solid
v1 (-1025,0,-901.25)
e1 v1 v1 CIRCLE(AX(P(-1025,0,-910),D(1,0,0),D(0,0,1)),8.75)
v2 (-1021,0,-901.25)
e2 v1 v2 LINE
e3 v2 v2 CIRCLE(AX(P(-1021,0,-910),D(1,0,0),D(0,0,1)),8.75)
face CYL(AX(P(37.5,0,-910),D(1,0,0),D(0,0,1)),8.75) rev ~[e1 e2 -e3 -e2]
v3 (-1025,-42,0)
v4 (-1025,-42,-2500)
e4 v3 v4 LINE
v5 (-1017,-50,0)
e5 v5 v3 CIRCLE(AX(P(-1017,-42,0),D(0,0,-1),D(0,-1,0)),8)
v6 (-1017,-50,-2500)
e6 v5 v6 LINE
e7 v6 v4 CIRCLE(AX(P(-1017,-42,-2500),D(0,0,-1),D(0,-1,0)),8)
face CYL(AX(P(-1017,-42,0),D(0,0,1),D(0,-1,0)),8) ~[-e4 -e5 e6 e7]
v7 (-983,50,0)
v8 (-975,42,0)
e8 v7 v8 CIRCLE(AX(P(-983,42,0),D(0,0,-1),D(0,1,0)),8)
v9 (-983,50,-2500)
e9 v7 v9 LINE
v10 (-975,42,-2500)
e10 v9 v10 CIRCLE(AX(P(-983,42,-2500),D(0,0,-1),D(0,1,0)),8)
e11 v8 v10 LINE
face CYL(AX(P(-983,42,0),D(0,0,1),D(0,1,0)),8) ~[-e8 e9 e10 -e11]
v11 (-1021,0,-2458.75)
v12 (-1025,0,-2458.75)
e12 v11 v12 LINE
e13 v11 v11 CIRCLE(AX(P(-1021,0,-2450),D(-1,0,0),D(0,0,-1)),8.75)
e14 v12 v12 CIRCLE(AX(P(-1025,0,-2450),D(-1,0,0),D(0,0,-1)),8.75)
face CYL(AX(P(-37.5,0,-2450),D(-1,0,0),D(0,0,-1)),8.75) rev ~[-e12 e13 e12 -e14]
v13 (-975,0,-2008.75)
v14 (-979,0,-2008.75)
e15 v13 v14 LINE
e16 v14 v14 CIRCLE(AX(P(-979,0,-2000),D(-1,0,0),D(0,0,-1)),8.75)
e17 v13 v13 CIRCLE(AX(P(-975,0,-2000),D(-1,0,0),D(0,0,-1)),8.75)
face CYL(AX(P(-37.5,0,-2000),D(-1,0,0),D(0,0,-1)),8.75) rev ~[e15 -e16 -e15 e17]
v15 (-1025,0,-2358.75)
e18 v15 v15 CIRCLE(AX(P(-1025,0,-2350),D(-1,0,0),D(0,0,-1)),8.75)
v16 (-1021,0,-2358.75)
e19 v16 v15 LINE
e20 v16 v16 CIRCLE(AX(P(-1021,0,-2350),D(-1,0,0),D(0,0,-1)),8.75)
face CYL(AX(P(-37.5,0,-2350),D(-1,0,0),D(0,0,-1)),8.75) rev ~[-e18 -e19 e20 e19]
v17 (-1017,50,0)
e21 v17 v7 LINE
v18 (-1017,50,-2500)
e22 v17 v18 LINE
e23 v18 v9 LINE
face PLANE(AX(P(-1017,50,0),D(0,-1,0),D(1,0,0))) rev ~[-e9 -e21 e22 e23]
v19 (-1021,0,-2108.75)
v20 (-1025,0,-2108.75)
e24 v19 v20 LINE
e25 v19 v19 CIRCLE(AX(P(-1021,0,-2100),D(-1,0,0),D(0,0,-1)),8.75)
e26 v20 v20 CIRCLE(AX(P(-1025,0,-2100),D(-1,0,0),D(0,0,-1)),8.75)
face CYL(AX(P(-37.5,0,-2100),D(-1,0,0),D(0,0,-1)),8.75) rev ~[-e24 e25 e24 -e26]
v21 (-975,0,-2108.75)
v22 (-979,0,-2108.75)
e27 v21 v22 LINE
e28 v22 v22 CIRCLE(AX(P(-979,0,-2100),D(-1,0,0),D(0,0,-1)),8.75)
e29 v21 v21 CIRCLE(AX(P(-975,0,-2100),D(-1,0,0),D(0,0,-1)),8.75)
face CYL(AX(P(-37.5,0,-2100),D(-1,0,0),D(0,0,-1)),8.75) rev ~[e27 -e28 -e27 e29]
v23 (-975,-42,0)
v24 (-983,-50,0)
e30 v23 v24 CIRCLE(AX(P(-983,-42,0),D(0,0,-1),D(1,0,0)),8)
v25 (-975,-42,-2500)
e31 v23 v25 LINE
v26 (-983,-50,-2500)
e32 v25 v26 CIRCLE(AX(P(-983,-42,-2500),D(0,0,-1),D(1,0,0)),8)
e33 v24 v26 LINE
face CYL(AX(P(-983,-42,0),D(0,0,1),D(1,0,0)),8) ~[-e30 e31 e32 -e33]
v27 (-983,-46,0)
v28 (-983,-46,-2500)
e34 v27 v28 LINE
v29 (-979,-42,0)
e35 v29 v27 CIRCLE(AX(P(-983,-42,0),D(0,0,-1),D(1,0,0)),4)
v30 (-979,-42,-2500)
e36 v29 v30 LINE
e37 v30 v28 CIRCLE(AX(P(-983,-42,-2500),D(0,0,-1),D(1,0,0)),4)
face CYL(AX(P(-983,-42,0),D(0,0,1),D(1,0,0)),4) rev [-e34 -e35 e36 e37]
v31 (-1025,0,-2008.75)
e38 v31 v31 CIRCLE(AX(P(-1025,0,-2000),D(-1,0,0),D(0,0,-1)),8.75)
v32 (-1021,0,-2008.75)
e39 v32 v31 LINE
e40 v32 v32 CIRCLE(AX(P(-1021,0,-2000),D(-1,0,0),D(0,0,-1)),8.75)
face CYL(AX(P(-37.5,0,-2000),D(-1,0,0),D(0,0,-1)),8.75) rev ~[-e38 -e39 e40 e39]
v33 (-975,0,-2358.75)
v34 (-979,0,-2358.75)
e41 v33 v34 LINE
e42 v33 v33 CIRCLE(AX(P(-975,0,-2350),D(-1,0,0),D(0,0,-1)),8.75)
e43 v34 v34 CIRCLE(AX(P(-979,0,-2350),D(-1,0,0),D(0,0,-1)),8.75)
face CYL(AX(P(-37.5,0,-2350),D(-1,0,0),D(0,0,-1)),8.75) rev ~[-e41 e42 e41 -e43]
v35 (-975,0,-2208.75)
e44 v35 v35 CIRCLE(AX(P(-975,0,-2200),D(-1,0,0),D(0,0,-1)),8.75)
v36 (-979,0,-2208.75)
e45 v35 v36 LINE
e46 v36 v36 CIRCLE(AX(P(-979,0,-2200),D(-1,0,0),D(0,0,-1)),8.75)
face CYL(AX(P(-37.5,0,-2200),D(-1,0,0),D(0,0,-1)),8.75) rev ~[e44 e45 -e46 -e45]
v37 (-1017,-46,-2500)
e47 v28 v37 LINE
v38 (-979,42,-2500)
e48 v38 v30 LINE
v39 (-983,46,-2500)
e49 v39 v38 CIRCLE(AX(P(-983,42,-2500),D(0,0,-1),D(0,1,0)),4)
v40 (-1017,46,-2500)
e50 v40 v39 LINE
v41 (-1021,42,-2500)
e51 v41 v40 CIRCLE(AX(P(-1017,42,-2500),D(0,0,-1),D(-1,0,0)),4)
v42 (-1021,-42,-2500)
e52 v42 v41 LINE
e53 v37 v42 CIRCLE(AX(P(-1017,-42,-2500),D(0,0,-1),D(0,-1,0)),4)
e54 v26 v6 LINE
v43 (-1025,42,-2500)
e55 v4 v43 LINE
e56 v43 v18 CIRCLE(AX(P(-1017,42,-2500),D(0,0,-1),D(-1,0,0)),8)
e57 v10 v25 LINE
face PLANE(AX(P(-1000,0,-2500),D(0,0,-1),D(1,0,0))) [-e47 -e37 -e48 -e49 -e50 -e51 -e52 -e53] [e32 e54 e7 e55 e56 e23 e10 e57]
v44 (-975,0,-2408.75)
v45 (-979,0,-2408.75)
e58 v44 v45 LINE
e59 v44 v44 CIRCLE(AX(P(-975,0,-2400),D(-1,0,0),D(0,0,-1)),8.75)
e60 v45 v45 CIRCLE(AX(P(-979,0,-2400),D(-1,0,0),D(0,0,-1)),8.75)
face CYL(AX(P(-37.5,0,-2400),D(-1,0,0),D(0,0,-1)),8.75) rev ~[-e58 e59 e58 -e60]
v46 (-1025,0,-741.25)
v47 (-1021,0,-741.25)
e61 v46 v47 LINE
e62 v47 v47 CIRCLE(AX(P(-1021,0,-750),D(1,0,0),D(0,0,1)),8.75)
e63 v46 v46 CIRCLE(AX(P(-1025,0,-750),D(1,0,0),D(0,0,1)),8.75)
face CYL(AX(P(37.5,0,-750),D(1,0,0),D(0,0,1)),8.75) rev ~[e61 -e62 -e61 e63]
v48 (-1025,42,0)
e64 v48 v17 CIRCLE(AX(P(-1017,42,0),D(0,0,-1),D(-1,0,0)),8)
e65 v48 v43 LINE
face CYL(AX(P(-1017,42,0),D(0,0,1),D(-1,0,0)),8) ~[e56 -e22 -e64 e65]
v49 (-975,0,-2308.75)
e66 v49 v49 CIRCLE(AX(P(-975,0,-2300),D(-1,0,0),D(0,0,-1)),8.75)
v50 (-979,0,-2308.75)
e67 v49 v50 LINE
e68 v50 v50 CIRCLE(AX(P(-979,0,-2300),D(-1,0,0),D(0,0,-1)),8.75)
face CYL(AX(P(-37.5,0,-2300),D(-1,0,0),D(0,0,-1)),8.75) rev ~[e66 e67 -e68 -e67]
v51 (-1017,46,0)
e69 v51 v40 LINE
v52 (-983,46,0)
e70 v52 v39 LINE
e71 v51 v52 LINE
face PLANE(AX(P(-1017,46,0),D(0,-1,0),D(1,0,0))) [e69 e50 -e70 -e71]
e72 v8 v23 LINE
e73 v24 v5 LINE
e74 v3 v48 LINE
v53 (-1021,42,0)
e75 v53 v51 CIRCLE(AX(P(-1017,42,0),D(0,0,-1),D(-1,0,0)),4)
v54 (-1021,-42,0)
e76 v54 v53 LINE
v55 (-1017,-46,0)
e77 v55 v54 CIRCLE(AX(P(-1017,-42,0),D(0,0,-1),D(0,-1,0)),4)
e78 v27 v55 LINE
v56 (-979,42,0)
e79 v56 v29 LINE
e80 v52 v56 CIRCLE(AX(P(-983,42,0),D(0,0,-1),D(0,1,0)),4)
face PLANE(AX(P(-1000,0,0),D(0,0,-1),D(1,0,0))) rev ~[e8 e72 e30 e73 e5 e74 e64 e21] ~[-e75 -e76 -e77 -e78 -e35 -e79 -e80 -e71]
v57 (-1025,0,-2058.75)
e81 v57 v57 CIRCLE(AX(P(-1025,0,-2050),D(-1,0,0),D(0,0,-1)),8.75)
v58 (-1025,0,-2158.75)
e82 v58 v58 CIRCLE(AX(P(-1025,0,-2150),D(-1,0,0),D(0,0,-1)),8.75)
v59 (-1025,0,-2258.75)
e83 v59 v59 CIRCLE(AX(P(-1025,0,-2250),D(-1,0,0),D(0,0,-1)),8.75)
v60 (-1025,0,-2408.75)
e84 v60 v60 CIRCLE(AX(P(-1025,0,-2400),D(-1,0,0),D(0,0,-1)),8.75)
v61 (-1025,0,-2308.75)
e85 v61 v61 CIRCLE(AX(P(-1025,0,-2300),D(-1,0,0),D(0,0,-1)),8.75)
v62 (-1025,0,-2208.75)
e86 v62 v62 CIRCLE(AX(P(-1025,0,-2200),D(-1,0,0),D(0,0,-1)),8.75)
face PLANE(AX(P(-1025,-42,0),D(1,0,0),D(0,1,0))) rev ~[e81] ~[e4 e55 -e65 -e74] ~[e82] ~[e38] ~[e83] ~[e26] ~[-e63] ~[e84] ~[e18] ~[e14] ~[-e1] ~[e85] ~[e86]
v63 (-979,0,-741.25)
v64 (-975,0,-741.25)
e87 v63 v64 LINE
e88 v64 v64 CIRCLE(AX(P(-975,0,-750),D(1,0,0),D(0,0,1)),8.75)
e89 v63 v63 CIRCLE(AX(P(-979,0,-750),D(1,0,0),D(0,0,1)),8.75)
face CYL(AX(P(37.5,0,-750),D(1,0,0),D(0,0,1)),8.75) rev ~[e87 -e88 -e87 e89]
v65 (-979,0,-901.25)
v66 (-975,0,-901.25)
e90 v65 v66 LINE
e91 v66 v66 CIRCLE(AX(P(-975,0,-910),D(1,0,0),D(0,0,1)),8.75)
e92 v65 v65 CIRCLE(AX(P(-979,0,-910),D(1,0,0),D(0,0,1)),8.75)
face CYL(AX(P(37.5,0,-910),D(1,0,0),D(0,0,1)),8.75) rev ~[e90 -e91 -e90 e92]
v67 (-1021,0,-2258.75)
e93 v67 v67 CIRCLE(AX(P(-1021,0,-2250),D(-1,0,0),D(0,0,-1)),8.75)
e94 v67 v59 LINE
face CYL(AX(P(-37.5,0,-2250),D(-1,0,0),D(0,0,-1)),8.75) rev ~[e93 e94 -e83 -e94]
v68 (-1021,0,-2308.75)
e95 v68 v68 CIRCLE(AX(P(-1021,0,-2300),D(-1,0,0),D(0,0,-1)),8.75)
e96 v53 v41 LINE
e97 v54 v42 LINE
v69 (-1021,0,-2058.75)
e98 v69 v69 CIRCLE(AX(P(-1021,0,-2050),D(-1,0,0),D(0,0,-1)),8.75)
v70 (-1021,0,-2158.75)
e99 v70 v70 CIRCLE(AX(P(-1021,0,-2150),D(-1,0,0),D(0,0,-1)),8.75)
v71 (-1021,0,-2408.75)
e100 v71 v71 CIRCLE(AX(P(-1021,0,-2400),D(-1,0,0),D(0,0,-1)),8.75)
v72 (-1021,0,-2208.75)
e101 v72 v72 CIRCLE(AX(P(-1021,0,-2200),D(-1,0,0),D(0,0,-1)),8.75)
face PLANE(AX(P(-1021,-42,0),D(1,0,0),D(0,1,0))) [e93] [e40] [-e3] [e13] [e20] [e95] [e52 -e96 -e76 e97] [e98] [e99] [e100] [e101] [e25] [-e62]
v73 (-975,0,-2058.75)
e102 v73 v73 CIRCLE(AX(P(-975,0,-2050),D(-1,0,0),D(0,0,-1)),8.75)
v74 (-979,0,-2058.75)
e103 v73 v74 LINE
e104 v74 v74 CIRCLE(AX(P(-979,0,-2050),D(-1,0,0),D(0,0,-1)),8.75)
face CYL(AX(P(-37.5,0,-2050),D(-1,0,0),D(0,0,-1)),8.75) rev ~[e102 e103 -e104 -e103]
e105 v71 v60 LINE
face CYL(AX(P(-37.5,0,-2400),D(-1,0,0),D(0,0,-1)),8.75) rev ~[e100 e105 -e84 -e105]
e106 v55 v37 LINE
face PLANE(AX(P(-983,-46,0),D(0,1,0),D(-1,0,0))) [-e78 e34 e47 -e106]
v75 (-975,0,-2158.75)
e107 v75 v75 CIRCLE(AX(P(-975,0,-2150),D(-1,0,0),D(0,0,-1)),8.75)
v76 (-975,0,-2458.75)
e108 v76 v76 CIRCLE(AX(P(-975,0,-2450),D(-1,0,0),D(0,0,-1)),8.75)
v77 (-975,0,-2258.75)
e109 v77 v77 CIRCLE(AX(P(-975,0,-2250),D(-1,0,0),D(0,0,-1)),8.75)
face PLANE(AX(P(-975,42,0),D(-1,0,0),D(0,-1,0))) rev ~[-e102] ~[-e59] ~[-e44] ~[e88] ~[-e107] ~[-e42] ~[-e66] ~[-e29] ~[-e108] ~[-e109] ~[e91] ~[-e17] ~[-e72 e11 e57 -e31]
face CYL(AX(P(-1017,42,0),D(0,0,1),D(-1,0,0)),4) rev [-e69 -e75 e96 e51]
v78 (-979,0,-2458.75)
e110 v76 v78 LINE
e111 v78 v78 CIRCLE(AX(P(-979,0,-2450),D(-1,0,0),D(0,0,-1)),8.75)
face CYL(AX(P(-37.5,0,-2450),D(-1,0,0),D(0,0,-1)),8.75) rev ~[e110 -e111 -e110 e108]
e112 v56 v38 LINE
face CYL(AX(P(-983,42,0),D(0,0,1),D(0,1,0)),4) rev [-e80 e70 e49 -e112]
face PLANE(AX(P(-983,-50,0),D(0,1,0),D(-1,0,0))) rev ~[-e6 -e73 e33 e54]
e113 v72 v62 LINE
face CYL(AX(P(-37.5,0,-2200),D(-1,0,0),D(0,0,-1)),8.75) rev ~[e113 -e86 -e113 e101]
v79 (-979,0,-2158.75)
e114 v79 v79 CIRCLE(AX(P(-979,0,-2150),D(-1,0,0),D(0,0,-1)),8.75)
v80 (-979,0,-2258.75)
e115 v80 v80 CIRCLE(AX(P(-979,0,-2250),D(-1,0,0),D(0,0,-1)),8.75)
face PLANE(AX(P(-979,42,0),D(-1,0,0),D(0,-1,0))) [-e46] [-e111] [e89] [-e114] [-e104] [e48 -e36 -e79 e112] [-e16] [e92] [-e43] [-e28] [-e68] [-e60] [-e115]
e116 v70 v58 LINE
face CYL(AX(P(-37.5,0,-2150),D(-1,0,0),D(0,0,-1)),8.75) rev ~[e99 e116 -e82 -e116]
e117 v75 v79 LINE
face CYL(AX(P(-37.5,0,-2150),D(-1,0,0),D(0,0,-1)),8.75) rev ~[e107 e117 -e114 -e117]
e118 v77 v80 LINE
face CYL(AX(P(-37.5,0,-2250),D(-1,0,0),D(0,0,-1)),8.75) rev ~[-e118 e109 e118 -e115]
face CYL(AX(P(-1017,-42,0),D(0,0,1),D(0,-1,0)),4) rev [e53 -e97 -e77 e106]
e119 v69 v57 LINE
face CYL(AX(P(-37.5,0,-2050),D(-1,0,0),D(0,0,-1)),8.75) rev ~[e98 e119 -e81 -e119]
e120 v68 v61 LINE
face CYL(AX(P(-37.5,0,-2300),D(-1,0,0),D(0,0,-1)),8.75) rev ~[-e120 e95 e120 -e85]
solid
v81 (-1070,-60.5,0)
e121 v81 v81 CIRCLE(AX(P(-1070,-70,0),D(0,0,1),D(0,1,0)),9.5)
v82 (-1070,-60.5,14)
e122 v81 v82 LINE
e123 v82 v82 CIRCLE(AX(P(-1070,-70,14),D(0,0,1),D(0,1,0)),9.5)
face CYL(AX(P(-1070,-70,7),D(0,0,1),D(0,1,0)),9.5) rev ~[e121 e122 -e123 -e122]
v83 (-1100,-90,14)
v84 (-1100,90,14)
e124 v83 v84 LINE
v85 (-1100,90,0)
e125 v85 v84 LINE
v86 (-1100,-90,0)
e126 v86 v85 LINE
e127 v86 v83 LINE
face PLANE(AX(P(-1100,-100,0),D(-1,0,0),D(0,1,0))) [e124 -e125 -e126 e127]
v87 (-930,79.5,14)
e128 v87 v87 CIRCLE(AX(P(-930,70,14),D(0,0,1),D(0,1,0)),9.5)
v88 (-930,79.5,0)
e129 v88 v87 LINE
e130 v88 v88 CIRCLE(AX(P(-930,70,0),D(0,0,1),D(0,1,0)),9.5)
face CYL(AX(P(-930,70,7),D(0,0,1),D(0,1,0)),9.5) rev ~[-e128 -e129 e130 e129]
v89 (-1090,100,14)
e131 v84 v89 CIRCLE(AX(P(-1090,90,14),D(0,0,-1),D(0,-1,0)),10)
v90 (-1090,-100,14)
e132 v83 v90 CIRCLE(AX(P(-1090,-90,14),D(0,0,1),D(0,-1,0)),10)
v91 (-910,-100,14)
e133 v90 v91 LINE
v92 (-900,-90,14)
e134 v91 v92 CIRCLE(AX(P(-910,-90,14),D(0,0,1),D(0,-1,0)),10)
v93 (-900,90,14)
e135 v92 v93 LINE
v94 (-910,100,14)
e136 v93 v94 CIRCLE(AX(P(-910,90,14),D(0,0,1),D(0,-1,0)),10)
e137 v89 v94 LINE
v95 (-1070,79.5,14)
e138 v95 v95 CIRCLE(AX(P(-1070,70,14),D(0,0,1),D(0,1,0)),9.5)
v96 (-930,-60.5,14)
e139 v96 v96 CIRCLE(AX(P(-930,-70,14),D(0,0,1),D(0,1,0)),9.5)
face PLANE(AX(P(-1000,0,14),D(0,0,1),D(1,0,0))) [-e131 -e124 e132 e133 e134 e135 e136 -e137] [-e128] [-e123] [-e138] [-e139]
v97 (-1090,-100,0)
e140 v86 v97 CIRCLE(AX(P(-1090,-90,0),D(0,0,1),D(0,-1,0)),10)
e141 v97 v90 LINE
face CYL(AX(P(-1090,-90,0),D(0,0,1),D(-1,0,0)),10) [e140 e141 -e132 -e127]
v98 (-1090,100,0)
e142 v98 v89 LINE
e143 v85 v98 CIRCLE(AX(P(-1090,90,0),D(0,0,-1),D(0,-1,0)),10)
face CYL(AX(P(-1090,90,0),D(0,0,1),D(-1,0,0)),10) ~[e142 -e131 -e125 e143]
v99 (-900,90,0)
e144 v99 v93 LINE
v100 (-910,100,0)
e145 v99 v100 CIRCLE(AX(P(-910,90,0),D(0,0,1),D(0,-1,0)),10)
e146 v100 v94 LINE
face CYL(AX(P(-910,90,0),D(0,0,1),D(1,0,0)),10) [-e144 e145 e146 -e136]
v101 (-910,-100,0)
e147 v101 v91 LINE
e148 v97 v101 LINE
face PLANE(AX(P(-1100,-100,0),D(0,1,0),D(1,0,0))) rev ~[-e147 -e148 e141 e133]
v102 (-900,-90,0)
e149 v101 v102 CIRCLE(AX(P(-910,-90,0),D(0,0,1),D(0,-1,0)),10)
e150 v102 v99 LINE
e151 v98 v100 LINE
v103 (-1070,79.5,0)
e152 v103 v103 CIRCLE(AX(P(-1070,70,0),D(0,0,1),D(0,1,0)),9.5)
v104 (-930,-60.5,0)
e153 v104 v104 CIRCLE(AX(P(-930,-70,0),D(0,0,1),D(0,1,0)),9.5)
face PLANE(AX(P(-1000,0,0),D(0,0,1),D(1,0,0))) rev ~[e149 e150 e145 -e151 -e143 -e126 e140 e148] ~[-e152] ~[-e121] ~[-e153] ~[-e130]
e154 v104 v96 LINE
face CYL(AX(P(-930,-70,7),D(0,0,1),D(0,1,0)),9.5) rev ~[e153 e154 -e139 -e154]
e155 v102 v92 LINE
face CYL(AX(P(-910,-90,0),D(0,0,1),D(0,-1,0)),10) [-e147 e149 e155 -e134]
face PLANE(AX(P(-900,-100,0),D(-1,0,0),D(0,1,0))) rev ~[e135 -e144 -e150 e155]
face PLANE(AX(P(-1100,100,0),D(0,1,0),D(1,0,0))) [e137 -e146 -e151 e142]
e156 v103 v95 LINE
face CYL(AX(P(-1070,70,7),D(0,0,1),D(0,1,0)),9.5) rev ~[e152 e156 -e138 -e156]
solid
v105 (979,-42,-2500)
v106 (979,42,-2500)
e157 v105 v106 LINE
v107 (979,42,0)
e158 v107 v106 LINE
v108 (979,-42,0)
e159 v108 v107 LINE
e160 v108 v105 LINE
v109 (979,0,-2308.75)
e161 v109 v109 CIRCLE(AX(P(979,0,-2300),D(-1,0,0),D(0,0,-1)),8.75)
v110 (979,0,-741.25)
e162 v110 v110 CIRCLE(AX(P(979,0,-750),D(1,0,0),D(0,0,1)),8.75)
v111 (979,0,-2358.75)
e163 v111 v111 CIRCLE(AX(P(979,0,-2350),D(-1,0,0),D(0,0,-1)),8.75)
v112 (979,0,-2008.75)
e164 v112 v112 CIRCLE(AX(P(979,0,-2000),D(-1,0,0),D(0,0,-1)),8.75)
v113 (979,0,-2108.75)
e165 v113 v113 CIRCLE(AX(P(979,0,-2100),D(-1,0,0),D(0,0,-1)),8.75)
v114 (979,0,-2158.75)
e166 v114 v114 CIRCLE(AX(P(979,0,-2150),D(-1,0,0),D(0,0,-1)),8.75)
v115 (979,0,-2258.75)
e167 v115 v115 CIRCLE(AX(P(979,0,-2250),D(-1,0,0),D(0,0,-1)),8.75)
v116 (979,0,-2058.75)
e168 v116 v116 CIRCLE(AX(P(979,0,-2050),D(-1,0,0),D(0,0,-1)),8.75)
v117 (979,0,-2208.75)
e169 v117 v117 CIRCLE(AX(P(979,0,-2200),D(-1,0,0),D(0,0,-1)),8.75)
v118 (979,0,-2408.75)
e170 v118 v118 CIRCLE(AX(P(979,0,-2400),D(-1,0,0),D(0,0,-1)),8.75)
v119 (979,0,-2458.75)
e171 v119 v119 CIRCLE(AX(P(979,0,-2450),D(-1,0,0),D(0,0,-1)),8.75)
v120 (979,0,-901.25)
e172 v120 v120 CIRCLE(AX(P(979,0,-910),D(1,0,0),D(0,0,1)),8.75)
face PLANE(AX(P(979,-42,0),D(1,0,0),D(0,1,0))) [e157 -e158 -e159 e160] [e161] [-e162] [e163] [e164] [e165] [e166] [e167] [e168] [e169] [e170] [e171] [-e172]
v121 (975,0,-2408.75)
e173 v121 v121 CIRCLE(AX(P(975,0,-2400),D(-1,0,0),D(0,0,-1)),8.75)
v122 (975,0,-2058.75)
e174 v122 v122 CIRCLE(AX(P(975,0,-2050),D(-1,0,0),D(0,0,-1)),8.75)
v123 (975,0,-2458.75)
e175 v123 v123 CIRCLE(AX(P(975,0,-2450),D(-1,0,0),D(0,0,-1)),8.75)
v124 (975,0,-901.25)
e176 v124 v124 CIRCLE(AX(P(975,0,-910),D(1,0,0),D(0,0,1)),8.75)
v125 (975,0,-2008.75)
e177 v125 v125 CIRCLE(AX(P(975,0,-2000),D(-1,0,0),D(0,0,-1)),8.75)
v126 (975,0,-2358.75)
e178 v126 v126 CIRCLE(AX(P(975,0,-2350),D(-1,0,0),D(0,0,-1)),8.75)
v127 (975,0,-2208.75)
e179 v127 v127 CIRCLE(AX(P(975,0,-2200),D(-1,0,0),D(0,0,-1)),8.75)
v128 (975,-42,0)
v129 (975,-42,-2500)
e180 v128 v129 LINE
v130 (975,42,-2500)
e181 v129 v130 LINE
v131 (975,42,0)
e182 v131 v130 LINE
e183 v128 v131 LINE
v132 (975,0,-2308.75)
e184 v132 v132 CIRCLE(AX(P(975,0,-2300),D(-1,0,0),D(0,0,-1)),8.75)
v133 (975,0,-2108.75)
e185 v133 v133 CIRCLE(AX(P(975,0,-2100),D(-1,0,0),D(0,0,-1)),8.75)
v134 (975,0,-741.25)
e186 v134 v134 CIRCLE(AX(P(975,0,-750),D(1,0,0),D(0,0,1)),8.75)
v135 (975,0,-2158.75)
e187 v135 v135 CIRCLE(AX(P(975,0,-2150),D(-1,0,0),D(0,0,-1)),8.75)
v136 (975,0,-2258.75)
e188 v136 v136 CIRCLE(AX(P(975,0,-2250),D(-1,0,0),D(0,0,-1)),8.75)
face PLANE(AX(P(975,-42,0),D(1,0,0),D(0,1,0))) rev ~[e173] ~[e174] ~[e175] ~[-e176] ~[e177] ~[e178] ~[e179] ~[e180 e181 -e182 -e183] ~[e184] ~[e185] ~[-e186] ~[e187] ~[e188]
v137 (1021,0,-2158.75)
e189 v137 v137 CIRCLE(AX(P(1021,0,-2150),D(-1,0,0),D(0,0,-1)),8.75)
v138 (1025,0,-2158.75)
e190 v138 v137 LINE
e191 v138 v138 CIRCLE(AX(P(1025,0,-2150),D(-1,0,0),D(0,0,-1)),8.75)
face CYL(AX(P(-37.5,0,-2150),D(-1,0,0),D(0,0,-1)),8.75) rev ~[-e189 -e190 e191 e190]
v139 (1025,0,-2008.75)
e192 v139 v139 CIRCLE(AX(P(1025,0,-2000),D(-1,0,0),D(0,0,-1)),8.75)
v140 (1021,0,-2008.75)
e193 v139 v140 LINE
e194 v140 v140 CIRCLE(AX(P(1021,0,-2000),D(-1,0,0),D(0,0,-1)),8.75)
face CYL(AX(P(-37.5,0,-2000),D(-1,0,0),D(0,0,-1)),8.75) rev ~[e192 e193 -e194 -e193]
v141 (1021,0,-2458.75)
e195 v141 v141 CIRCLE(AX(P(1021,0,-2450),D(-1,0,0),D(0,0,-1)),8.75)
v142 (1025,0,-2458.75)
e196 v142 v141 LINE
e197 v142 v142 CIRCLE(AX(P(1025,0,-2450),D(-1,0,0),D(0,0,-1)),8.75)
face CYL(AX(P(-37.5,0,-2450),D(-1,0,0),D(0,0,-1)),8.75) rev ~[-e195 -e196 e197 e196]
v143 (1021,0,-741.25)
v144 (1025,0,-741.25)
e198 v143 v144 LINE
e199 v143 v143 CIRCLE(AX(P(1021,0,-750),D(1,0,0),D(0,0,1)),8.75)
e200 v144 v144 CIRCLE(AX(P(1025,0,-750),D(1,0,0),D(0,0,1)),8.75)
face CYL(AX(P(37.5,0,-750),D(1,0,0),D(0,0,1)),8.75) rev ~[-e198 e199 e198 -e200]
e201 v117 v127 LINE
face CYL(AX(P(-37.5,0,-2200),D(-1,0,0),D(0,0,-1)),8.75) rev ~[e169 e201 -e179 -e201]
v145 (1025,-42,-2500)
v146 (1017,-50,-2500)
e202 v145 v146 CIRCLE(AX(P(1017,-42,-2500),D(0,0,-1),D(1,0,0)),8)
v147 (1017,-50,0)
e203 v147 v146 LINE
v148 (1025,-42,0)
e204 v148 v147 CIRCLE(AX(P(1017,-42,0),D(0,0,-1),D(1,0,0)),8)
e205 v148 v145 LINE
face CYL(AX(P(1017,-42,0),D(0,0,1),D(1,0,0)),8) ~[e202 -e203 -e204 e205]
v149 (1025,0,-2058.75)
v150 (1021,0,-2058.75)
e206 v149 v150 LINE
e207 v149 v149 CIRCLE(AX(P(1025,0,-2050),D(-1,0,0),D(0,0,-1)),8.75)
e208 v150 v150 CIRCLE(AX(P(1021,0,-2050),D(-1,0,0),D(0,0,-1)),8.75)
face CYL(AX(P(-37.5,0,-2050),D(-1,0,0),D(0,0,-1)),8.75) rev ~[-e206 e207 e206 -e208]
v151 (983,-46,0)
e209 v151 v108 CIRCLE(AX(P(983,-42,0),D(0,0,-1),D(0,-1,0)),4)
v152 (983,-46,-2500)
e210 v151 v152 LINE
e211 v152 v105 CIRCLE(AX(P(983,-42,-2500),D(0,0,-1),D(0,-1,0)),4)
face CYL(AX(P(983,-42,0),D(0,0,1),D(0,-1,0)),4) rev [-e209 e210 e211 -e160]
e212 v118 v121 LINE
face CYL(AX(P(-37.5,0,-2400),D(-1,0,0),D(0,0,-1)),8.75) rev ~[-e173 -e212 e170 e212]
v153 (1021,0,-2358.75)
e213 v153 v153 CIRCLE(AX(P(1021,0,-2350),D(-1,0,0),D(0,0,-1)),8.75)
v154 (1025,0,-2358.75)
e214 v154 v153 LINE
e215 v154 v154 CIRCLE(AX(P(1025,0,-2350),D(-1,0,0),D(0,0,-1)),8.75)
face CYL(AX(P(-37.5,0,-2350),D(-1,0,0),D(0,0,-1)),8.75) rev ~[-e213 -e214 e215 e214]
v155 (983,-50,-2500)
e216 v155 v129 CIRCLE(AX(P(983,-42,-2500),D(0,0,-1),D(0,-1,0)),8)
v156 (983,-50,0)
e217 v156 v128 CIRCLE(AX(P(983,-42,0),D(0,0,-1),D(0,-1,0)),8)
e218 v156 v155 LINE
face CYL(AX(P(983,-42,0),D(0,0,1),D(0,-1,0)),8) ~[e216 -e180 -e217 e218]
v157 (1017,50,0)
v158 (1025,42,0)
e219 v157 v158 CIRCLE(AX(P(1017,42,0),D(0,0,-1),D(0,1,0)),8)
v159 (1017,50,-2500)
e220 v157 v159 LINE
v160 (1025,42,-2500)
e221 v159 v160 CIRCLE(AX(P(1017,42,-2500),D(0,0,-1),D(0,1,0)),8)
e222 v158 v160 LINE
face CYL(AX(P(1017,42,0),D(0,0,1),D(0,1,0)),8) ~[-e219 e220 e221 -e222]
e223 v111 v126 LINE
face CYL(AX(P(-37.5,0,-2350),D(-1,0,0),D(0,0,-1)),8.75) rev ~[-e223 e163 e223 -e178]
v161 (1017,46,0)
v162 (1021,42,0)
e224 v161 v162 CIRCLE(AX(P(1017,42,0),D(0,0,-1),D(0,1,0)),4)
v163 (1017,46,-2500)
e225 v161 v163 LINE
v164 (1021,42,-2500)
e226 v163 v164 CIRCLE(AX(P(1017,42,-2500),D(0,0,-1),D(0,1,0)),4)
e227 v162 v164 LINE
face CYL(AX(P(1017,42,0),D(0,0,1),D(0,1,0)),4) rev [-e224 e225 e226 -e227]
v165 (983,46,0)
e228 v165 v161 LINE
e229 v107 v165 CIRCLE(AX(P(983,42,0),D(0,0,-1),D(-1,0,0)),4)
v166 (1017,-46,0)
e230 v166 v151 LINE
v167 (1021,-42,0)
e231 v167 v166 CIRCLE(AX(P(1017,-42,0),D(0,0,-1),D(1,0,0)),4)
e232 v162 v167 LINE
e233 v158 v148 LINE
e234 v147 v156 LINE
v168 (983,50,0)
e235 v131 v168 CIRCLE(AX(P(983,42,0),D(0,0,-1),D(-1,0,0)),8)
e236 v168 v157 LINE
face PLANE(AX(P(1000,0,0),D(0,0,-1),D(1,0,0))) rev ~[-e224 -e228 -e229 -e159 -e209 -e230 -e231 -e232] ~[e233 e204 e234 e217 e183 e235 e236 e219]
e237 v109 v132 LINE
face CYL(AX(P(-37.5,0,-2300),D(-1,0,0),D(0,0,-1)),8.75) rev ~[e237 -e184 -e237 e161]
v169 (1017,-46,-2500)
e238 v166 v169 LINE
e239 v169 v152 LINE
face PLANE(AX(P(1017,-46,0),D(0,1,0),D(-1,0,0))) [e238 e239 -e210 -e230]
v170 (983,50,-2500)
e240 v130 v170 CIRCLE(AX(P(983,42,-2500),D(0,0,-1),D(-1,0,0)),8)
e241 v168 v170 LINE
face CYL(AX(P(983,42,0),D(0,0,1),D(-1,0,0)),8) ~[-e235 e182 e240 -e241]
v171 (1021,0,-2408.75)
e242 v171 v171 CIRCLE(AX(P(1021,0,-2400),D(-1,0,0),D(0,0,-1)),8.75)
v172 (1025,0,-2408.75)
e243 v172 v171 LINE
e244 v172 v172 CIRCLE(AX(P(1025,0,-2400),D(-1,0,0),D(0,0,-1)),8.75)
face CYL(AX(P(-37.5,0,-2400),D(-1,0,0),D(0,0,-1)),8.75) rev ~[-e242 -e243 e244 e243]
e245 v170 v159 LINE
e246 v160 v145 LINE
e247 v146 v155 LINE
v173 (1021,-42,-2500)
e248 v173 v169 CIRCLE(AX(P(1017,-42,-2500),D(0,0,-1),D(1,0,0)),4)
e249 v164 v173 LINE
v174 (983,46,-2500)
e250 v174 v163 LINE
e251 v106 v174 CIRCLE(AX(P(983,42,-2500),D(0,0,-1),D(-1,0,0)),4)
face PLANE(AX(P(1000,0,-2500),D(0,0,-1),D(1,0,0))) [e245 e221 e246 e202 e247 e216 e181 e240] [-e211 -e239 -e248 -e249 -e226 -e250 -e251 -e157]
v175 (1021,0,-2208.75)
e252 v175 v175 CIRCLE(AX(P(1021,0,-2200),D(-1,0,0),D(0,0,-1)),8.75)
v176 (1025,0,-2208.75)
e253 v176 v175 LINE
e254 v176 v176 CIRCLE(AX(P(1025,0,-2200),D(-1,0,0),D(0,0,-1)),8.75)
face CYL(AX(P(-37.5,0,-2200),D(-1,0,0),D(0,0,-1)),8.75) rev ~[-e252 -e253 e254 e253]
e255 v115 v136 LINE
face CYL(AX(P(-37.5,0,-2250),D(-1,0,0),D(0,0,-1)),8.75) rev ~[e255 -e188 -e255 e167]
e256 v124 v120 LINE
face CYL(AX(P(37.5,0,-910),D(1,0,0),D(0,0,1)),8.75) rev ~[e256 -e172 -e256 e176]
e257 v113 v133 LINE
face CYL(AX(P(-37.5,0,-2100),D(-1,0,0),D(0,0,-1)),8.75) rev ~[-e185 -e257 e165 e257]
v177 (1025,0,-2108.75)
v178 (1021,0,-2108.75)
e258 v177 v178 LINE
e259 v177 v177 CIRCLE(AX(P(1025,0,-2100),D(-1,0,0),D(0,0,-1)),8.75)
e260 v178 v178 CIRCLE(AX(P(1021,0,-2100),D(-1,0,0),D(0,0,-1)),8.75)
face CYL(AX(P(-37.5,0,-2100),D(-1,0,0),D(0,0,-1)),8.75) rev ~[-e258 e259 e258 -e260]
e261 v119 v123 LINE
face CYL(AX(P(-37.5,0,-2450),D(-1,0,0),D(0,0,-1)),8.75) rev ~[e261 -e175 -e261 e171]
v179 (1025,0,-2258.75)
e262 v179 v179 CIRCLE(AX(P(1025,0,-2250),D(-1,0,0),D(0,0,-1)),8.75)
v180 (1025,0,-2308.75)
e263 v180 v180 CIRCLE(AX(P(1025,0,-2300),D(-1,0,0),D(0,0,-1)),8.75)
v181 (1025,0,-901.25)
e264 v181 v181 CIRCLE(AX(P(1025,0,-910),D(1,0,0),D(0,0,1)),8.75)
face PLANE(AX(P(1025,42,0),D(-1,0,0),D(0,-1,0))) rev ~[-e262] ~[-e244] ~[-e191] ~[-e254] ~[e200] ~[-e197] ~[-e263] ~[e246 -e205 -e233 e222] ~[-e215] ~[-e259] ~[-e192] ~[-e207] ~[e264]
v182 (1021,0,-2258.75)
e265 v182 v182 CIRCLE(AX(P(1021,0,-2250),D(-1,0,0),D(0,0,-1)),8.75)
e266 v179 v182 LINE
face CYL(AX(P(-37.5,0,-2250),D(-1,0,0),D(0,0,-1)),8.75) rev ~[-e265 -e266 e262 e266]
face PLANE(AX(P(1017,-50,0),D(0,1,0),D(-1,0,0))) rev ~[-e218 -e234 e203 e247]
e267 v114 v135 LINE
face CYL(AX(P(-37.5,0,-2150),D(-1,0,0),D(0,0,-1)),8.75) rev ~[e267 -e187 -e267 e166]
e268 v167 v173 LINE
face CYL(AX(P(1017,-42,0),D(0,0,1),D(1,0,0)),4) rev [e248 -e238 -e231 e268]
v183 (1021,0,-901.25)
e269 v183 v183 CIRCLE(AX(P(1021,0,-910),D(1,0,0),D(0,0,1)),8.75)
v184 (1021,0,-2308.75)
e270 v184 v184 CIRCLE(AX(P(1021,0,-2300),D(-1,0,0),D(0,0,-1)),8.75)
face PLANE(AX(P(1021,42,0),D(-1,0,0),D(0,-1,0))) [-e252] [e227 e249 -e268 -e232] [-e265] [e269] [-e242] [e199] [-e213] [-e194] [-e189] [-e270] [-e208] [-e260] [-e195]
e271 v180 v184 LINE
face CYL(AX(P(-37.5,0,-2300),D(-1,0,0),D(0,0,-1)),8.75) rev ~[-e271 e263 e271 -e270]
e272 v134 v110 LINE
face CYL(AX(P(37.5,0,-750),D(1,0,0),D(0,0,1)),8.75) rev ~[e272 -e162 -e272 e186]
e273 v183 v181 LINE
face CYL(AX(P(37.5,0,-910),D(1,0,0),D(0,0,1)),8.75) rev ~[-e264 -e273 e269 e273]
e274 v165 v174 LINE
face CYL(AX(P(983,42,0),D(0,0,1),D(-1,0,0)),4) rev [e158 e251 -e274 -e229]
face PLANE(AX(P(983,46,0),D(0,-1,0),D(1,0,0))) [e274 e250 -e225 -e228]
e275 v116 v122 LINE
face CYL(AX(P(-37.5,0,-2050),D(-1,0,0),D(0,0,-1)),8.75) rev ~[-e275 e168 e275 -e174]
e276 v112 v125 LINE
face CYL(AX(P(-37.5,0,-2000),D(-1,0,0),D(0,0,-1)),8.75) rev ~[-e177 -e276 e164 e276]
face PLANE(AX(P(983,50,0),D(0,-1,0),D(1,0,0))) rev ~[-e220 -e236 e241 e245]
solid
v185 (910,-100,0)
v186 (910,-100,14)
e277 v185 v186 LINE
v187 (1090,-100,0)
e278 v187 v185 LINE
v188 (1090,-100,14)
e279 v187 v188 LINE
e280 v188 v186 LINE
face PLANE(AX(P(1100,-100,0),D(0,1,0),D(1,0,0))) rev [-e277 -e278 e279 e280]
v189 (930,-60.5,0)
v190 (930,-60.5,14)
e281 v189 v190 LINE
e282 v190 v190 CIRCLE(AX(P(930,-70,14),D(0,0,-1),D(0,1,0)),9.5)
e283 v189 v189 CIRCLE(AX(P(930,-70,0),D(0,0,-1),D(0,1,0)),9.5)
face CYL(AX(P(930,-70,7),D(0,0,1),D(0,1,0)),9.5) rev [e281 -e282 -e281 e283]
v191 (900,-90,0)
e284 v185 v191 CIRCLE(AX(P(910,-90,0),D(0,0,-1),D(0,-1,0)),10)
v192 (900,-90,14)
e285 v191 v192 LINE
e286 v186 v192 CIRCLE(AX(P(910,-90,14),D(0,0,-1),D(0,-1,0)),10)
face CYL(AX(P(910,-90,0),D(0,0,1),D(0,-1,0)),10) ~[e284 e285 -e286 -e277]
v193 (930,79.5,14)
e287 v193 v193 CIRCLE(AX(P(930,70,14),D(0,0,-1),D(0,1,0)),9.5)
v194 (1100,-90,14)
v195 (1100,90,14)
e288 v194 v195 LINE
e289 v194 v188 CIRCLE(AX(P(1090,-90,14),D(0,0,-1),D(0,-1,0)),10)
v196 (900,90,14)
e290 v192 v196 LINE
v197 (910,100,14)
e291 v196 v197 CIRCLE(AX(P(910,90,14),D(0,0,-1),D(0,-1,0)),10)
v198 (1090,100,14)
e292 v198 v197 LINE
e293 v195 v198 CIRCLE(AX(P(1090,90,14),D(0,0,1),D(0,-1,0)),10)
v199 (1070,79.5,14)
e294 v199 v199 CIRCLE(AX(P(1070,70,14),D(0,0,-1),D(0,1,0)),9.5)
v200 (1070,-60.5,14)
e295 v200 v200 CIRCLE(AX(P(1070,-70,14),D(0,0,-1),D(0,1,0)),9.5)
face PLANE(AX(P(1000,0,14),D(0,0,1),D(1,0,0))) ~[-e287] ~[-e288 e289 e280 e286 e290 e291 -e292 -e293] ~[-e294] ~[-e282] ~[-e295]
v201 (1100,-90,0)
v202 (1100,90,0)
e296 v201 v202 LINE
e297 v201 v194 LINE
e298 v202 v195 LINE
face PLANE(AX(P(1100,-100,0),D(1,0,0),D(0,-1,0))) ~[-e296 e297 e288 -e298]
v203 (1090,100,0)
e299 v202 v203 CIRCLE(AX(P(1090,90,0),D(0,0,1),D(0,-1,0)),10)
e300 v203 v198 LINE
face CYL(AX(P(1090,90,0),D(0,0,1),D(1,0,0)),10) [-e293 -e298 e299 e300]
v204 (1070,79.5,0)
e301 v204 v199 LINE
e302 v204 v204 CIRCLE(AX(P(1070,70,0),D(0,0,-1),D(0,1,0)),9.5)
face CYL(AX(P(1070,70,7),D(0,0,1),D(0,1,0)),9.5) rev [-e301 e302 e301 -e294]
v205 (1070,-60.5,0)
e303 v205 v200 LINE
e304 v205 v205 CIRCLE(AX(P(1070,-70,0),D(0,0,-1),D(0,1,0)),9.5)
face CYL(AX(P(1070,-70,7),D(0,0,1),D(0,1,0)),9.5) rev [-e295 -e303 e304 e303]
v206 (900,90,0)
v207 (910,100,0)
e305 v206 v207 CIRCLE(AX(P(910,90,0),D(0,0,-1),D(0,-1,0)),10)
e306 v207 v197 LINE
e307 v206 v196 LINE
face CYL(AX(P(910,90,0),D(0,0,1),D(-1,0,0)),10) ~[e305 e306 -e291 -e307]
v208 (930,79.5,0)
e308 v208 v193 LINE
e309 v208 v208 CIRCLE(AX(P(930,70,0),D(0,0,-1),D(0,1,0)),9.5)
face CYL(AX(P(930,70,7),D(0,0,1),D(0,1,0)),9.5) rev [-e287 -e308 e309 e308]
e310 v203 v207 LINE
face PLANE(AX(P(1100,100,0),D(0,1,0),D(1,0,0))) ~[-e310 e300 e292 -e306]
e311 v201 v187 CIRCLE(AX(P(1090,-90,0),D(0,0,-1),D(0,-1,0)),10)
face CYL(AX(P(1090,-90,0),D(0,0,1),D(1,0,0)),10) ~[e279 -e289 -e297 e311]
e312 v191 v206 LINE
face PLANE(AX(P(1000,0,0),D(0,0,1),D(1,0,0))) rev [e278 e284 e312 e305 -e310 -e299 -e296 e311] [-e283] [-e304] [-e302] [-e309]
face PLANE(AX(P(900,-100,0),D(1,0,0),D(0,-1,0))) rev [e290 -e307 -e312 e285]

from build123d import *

# Parameters (mm, degrees)
GB_6728_1986_RECTANGULAR_HOLLOW_SECTION_DEPTH = 2500
GB_6728_1986_RECTANGULAR_HOLLOW_SECT_2_DEPTH  = 2500
SKETCH5_W                                     = 200
SKETCH5_H                                     = 200
BOSS_EXTRUDE1_DEPTH                           = 14
FILLET1_R                                     = 10
SKETCH9_W                                     = 9.5
SKETCH9_H                                     = 14
M16_CLEARANCE_HOLE1_AT_2_COUNT                = 2
M16_CLEARANCE_HOLE1_AT_2_PITCH                = 140
M16_CLEARANCE_HOLE1_AT_3_COUNT                = 2
M16_CLEARANCE_HOLE1_AT_3_PITCH                = 197.989898732
M16_CLEARANCE_HOLE1_AT_4_COUNT                = 2
M16_CLEARANCE_HOLE1_AT_4_PITCH                = 140
SKETCH14_W                                    = 8.75
SKETCH14_H                                    = 2125
LPATTERN1_COUNT                               = 10
LPATTERN1_PITCH                               = 50
SKETCH16_W                                    = 8.75
SKETCH16_H                                    = 2125
M16_CLEARANCE_HOLE4_AT_2_COUNT                = 2
M16_CLEARANCE_HOLE4_AT_2_PITCH                = 160


with BuildPart() as part:
    # Sketch12 → Gb／6728-1986 rectangular hollow section 100 X 50 X 4 (1) (new body)
    with BuildSketch(Plane(origin=(-1000, 0, 0), x_dir=(1, 0, 0), z_dir=(0, 0, -1))):
        with BuildLine():
            Line((-17, -50), (17, -50))
            ThreePointArc((17, -50), (22.656854249, -47.656854249), (25, -42))
            Line((25, -42), (25, 42))
            ThreePointArc((25, 42), (22.656854249, 47.656854249), (17, 50))
            Line((17, 50), (-17, 50))
            ThreePointArc((-17, 50), (-22.656854249, 47.656854249), (-25, 42))
            Line((-25, 42), (-25, -42))
            ThreePointArc((-25, -42), (-22.656854249, -47.656854249), (-17, -50))
        make_face()
        with BuildLine():
            Line((-17, -46), (17, -46))
            ThreePointArc((17, -46), (19.828427125, -44.828427125), (21, -42))
            Line((21, -42), (21, 42))
            ThreePointArc((21, 42), (19.828427125, 44.828427125), (17, 46))
            Line((17, 46), (-17, 46))
            ThreePointArc((-17, 46), (-19.828427125, 44.828427125), (-21, 42))
            Line((-21, 42), (-21, -42))
            ThreePointArc((-21, -42), (-19.828427125, -44.828427125), (-17, -46))
        make_face(mode=Mode.SUBTRACT)
    extrude(amount=GB_6728_1986_RECTANGULAR_HOLLOW_SECTION_DEPTH)


with BuildPart() as body_2:
    # Sketch12 on segment 2 (carried to segment 2) → Gb_6728-1986 rectangular hollow sect 2 (new body)
    with BuildSketch(Plane(origin=(1000, 0, 0), x_dir=(1, 0, 0), z_dir=(0, 0, -1))):
        with BuildLine():
            Line((-17, -50), (17, -50))
            ThreePointArc((17, -50), (22.656854249, -47.656854249), (25, -42))
            Line((25, -42), (25, 42))
            ThreePointArc((25, 42), (22.656854249, 47.656854249), (17, 50))
            Line((17, 50), (-17, 50))
            ThreePointArc((-17, 50), (-22.656854249, 47.656854249), (-25, 42))
            Line((-25, 42), (-25, -42))
            ThreePointArc((-25, -42), (-22.656854249, -47.656854249), (-17, -50))
        make_face()
        with BuildLine():
            Line((-17, -46), (17, -46))
            ThreePointArc((17, -46), (19.828427125, -44.828427125), (21, -42))
            Line((21, -42), (21, 42))
            ThreePointArc((21, 42), (19.828427125, 44.828427125), (17, 46))
            Line((17, 46), (-17, 46))
            ThreePointArc((-17, 46), (-19.828427125, 44.828427125), (-21, 42))
            Line((-21, 42), (-21, -42))
            ThreePointArc((-21, -42), (-19.828427125, -44.828427125), (-17, -46))
        make_face(mode=Mode.SUBTRACT)
    extrude(amount=GB_6728_1986_RECTANGULAR_HOLLOW_SECT_2_DEPTH)


with BuildPart() as body_3:
    # Sketch5 → Boss-Extrude1 (new body)
    with BuildSketch(Plane.XY):
        with Locations((-1000, 0)):
            Rectangle(SKETCH5_W, SKETCH5_H)
    extrude(amount=BOSS_EXTRUDE1_DEPTH)

    # Fillet1
    fillet1_edges = [body_3.edges().sort_by_distance(p)[0] for p in [
        (-900, -100, 7),
        (-1100, -100, 7),
        (-1100, 100, 7),
        (-900, 100, 7),
    ]]
    fillet(fillet1_edges, radius=FILLET1_R)

    # Sketch9 → M16 Clearance Hole1 (revolve, cut)
    with BuildSketch(Plane(origin=(-1070, 70, 0), x_dir=(0, 1, 0), z_dir=(1, 0, 0))):
        with Locations((4.75, 7)):
            Rectangle(SKETCH9_W, SKETCH9_H)
    m16_clearance_hole1 = revolve(axis=Axis((-1070, 70, -6.35), (0, 0, 1)), mode=Mode.SUBTRACT)

    # M16 Clearance Hole1 at 2: M16 Clearance Hole1 ×2
    with Locations(*[(0, -i * M16_CLEARANCE_HOLE1_AT_2_PITCH, 0) for i in range(1, M16_CLEARANCE_HOLE1_AT_2_COUNT)]):
        add(m16_clearance_hole1, mode=Mode.SUBTRACT)

    # M16 Clearance Hole1 at 3: M16 Clearance Hole1 ×2
    with Locations(*[Vector(0.7071067811865475, -0.7071067811865477, 0) * (i * M16_CLEARANCE_HOLE1_AT_3_PITCH) for i in range(1, M16_CLEARANCE_HOLE1_AT_3_COUNT)]):
        add(m16_clearance_hole1, mode=Mode.SUBTRACT)

    # M16 Clearance Hole1 at 4: M16 Clearance Hole1 ×2
    with Locations(*[(i * M16_CLEARANCE_HOLE1_AT_4_PITCH, 0, 0) for i in range(1, M16_CLEARANCE_HOLE1_AT_4_COUNT)]):
        add(m16_clearance_hole1, mode=Mode.SUBTRACT)


with BuildPart() as body_4:
    # Mirror1: mirrored copy
    add(body_3.part.mirror(Plane.ZY))


with BuildPart() as m16_clearance_hole3_tool:
    # Sketch14 → M16 Clearance Hole3 (revolve)
    with BuildSketch(Plane(origin=(1025, 0, -2450), x_dir=(0, 0, -1), z_dir=(0, 1, 0))):
        with Locations((4.375, 1062.5)):
            Rectangle(SKETCH14_W, SKETCH14_H)
    m16_clearance_hole3 = revolve(axis=Axis((1031.35, 0, -2450), (-1, 0, 0)))


with BuildPart() as part_1:
    add(part.part)

    # M16 Clearance Hole3: cut by m16_clearance_hole3_tool
    add(m16_clearance_hole3_tool.part, mode=Mode.SUBTRACT)


with BuildPart() as body_2_1:
    add(body_2.part)

    # M16 Clearance Hole3: cut by m16_clearance_hole3_tool
    add(m16_clearance_hole3_tool.part, mode=Mode.SUBTRACT)


with BuildPart() as lpattern1_tool:
    # LPattern1: M16 Clearance Hole3 ×10
    with Locations(*[(0, 0, i * LPATTERN1_PITCH) for i in range(1, LPATTERN1_COUNT)]):
        add(m16_clearance_hole3)


with BuildPart() as part_2:
    add(part_1.part)

    # LPattern1: cut by lpattern1_tool
    add(lpattern1_tool.part, mode=Mode.SUBTRACT)


with BuildPart() as body_2_2:
    add(body_2_1.part)

    # LPattern1: cut by lpattern1_tool
    add(lpattern1_tool.part, mode=Mode.SUBTRACT)


with BuildPart() as m16_clearance_hole4_tool:
    # Sketch16 → M16 Clearance Hole4 (revolve)
    with BuildSketch(Plane(origin=(-1025, 0, -750), x_dir=(0, 0, 1), z_dir=(0, 1, 0))):
        with Locations((4.375, 1062.5)):
            Rectangle(SKETCH16_W, SKETCH16_H)
    m16_clearance_hole4 = revolve(axis=Axis((-1031.35, 0, -750), (1, 0, 0)))


with BuildPart() as part_3:
    add(part_2.part)

    # M16 Clearance Hole4: cut by m16_clearance_hole4_tool
    add(m16_clearance_hole4_tool.part, mode=Mode.SUBTRACT)


with BuildPart() as body_2_3:
    add(body_2_2.part)

    # M16 Clearance Hole4: cut by m16_clearance_hole4_tool
    add(m16_clearance_hole4_tool.part, mode=Mode.SUBTRACT)


with BuildPart() as m16_clearance_hole4_at_2_tool:
    # M16 Clearance Hole4 at 2: M16 Clearance Hole4 ×2
    with Locations(*[(0, 0, -i * M16_CLEARANCE_HOLE4_AT_2_PITCH) for i in range(1, M16_CLEARANCE_HOLE4_AT_2_COUNT)]):
        add(m16_clearance_hole4)


with BuildPart() as part_4:
    add(part_3.part)

    # M16 Clearance Hole4 at 2: cut by m16_clearance_hole4_at_2_tool
    add(m16_clearance_hole4_at_2_tool.part, mode=Mode.SUBTRACT)


with BuildPart() as body_2_4:
    add(body_2_3.part)

    # M16 Clearance Hole4 at 2: cut by m16_clearance_hole4_at_2_tool
    add(m16_clearance_hole4_at_2_tool.part, mode=Mode.SUBTRACT)


solid = Compound([body_3.part, body_4.part, part_4.part, body_2_4.part])
